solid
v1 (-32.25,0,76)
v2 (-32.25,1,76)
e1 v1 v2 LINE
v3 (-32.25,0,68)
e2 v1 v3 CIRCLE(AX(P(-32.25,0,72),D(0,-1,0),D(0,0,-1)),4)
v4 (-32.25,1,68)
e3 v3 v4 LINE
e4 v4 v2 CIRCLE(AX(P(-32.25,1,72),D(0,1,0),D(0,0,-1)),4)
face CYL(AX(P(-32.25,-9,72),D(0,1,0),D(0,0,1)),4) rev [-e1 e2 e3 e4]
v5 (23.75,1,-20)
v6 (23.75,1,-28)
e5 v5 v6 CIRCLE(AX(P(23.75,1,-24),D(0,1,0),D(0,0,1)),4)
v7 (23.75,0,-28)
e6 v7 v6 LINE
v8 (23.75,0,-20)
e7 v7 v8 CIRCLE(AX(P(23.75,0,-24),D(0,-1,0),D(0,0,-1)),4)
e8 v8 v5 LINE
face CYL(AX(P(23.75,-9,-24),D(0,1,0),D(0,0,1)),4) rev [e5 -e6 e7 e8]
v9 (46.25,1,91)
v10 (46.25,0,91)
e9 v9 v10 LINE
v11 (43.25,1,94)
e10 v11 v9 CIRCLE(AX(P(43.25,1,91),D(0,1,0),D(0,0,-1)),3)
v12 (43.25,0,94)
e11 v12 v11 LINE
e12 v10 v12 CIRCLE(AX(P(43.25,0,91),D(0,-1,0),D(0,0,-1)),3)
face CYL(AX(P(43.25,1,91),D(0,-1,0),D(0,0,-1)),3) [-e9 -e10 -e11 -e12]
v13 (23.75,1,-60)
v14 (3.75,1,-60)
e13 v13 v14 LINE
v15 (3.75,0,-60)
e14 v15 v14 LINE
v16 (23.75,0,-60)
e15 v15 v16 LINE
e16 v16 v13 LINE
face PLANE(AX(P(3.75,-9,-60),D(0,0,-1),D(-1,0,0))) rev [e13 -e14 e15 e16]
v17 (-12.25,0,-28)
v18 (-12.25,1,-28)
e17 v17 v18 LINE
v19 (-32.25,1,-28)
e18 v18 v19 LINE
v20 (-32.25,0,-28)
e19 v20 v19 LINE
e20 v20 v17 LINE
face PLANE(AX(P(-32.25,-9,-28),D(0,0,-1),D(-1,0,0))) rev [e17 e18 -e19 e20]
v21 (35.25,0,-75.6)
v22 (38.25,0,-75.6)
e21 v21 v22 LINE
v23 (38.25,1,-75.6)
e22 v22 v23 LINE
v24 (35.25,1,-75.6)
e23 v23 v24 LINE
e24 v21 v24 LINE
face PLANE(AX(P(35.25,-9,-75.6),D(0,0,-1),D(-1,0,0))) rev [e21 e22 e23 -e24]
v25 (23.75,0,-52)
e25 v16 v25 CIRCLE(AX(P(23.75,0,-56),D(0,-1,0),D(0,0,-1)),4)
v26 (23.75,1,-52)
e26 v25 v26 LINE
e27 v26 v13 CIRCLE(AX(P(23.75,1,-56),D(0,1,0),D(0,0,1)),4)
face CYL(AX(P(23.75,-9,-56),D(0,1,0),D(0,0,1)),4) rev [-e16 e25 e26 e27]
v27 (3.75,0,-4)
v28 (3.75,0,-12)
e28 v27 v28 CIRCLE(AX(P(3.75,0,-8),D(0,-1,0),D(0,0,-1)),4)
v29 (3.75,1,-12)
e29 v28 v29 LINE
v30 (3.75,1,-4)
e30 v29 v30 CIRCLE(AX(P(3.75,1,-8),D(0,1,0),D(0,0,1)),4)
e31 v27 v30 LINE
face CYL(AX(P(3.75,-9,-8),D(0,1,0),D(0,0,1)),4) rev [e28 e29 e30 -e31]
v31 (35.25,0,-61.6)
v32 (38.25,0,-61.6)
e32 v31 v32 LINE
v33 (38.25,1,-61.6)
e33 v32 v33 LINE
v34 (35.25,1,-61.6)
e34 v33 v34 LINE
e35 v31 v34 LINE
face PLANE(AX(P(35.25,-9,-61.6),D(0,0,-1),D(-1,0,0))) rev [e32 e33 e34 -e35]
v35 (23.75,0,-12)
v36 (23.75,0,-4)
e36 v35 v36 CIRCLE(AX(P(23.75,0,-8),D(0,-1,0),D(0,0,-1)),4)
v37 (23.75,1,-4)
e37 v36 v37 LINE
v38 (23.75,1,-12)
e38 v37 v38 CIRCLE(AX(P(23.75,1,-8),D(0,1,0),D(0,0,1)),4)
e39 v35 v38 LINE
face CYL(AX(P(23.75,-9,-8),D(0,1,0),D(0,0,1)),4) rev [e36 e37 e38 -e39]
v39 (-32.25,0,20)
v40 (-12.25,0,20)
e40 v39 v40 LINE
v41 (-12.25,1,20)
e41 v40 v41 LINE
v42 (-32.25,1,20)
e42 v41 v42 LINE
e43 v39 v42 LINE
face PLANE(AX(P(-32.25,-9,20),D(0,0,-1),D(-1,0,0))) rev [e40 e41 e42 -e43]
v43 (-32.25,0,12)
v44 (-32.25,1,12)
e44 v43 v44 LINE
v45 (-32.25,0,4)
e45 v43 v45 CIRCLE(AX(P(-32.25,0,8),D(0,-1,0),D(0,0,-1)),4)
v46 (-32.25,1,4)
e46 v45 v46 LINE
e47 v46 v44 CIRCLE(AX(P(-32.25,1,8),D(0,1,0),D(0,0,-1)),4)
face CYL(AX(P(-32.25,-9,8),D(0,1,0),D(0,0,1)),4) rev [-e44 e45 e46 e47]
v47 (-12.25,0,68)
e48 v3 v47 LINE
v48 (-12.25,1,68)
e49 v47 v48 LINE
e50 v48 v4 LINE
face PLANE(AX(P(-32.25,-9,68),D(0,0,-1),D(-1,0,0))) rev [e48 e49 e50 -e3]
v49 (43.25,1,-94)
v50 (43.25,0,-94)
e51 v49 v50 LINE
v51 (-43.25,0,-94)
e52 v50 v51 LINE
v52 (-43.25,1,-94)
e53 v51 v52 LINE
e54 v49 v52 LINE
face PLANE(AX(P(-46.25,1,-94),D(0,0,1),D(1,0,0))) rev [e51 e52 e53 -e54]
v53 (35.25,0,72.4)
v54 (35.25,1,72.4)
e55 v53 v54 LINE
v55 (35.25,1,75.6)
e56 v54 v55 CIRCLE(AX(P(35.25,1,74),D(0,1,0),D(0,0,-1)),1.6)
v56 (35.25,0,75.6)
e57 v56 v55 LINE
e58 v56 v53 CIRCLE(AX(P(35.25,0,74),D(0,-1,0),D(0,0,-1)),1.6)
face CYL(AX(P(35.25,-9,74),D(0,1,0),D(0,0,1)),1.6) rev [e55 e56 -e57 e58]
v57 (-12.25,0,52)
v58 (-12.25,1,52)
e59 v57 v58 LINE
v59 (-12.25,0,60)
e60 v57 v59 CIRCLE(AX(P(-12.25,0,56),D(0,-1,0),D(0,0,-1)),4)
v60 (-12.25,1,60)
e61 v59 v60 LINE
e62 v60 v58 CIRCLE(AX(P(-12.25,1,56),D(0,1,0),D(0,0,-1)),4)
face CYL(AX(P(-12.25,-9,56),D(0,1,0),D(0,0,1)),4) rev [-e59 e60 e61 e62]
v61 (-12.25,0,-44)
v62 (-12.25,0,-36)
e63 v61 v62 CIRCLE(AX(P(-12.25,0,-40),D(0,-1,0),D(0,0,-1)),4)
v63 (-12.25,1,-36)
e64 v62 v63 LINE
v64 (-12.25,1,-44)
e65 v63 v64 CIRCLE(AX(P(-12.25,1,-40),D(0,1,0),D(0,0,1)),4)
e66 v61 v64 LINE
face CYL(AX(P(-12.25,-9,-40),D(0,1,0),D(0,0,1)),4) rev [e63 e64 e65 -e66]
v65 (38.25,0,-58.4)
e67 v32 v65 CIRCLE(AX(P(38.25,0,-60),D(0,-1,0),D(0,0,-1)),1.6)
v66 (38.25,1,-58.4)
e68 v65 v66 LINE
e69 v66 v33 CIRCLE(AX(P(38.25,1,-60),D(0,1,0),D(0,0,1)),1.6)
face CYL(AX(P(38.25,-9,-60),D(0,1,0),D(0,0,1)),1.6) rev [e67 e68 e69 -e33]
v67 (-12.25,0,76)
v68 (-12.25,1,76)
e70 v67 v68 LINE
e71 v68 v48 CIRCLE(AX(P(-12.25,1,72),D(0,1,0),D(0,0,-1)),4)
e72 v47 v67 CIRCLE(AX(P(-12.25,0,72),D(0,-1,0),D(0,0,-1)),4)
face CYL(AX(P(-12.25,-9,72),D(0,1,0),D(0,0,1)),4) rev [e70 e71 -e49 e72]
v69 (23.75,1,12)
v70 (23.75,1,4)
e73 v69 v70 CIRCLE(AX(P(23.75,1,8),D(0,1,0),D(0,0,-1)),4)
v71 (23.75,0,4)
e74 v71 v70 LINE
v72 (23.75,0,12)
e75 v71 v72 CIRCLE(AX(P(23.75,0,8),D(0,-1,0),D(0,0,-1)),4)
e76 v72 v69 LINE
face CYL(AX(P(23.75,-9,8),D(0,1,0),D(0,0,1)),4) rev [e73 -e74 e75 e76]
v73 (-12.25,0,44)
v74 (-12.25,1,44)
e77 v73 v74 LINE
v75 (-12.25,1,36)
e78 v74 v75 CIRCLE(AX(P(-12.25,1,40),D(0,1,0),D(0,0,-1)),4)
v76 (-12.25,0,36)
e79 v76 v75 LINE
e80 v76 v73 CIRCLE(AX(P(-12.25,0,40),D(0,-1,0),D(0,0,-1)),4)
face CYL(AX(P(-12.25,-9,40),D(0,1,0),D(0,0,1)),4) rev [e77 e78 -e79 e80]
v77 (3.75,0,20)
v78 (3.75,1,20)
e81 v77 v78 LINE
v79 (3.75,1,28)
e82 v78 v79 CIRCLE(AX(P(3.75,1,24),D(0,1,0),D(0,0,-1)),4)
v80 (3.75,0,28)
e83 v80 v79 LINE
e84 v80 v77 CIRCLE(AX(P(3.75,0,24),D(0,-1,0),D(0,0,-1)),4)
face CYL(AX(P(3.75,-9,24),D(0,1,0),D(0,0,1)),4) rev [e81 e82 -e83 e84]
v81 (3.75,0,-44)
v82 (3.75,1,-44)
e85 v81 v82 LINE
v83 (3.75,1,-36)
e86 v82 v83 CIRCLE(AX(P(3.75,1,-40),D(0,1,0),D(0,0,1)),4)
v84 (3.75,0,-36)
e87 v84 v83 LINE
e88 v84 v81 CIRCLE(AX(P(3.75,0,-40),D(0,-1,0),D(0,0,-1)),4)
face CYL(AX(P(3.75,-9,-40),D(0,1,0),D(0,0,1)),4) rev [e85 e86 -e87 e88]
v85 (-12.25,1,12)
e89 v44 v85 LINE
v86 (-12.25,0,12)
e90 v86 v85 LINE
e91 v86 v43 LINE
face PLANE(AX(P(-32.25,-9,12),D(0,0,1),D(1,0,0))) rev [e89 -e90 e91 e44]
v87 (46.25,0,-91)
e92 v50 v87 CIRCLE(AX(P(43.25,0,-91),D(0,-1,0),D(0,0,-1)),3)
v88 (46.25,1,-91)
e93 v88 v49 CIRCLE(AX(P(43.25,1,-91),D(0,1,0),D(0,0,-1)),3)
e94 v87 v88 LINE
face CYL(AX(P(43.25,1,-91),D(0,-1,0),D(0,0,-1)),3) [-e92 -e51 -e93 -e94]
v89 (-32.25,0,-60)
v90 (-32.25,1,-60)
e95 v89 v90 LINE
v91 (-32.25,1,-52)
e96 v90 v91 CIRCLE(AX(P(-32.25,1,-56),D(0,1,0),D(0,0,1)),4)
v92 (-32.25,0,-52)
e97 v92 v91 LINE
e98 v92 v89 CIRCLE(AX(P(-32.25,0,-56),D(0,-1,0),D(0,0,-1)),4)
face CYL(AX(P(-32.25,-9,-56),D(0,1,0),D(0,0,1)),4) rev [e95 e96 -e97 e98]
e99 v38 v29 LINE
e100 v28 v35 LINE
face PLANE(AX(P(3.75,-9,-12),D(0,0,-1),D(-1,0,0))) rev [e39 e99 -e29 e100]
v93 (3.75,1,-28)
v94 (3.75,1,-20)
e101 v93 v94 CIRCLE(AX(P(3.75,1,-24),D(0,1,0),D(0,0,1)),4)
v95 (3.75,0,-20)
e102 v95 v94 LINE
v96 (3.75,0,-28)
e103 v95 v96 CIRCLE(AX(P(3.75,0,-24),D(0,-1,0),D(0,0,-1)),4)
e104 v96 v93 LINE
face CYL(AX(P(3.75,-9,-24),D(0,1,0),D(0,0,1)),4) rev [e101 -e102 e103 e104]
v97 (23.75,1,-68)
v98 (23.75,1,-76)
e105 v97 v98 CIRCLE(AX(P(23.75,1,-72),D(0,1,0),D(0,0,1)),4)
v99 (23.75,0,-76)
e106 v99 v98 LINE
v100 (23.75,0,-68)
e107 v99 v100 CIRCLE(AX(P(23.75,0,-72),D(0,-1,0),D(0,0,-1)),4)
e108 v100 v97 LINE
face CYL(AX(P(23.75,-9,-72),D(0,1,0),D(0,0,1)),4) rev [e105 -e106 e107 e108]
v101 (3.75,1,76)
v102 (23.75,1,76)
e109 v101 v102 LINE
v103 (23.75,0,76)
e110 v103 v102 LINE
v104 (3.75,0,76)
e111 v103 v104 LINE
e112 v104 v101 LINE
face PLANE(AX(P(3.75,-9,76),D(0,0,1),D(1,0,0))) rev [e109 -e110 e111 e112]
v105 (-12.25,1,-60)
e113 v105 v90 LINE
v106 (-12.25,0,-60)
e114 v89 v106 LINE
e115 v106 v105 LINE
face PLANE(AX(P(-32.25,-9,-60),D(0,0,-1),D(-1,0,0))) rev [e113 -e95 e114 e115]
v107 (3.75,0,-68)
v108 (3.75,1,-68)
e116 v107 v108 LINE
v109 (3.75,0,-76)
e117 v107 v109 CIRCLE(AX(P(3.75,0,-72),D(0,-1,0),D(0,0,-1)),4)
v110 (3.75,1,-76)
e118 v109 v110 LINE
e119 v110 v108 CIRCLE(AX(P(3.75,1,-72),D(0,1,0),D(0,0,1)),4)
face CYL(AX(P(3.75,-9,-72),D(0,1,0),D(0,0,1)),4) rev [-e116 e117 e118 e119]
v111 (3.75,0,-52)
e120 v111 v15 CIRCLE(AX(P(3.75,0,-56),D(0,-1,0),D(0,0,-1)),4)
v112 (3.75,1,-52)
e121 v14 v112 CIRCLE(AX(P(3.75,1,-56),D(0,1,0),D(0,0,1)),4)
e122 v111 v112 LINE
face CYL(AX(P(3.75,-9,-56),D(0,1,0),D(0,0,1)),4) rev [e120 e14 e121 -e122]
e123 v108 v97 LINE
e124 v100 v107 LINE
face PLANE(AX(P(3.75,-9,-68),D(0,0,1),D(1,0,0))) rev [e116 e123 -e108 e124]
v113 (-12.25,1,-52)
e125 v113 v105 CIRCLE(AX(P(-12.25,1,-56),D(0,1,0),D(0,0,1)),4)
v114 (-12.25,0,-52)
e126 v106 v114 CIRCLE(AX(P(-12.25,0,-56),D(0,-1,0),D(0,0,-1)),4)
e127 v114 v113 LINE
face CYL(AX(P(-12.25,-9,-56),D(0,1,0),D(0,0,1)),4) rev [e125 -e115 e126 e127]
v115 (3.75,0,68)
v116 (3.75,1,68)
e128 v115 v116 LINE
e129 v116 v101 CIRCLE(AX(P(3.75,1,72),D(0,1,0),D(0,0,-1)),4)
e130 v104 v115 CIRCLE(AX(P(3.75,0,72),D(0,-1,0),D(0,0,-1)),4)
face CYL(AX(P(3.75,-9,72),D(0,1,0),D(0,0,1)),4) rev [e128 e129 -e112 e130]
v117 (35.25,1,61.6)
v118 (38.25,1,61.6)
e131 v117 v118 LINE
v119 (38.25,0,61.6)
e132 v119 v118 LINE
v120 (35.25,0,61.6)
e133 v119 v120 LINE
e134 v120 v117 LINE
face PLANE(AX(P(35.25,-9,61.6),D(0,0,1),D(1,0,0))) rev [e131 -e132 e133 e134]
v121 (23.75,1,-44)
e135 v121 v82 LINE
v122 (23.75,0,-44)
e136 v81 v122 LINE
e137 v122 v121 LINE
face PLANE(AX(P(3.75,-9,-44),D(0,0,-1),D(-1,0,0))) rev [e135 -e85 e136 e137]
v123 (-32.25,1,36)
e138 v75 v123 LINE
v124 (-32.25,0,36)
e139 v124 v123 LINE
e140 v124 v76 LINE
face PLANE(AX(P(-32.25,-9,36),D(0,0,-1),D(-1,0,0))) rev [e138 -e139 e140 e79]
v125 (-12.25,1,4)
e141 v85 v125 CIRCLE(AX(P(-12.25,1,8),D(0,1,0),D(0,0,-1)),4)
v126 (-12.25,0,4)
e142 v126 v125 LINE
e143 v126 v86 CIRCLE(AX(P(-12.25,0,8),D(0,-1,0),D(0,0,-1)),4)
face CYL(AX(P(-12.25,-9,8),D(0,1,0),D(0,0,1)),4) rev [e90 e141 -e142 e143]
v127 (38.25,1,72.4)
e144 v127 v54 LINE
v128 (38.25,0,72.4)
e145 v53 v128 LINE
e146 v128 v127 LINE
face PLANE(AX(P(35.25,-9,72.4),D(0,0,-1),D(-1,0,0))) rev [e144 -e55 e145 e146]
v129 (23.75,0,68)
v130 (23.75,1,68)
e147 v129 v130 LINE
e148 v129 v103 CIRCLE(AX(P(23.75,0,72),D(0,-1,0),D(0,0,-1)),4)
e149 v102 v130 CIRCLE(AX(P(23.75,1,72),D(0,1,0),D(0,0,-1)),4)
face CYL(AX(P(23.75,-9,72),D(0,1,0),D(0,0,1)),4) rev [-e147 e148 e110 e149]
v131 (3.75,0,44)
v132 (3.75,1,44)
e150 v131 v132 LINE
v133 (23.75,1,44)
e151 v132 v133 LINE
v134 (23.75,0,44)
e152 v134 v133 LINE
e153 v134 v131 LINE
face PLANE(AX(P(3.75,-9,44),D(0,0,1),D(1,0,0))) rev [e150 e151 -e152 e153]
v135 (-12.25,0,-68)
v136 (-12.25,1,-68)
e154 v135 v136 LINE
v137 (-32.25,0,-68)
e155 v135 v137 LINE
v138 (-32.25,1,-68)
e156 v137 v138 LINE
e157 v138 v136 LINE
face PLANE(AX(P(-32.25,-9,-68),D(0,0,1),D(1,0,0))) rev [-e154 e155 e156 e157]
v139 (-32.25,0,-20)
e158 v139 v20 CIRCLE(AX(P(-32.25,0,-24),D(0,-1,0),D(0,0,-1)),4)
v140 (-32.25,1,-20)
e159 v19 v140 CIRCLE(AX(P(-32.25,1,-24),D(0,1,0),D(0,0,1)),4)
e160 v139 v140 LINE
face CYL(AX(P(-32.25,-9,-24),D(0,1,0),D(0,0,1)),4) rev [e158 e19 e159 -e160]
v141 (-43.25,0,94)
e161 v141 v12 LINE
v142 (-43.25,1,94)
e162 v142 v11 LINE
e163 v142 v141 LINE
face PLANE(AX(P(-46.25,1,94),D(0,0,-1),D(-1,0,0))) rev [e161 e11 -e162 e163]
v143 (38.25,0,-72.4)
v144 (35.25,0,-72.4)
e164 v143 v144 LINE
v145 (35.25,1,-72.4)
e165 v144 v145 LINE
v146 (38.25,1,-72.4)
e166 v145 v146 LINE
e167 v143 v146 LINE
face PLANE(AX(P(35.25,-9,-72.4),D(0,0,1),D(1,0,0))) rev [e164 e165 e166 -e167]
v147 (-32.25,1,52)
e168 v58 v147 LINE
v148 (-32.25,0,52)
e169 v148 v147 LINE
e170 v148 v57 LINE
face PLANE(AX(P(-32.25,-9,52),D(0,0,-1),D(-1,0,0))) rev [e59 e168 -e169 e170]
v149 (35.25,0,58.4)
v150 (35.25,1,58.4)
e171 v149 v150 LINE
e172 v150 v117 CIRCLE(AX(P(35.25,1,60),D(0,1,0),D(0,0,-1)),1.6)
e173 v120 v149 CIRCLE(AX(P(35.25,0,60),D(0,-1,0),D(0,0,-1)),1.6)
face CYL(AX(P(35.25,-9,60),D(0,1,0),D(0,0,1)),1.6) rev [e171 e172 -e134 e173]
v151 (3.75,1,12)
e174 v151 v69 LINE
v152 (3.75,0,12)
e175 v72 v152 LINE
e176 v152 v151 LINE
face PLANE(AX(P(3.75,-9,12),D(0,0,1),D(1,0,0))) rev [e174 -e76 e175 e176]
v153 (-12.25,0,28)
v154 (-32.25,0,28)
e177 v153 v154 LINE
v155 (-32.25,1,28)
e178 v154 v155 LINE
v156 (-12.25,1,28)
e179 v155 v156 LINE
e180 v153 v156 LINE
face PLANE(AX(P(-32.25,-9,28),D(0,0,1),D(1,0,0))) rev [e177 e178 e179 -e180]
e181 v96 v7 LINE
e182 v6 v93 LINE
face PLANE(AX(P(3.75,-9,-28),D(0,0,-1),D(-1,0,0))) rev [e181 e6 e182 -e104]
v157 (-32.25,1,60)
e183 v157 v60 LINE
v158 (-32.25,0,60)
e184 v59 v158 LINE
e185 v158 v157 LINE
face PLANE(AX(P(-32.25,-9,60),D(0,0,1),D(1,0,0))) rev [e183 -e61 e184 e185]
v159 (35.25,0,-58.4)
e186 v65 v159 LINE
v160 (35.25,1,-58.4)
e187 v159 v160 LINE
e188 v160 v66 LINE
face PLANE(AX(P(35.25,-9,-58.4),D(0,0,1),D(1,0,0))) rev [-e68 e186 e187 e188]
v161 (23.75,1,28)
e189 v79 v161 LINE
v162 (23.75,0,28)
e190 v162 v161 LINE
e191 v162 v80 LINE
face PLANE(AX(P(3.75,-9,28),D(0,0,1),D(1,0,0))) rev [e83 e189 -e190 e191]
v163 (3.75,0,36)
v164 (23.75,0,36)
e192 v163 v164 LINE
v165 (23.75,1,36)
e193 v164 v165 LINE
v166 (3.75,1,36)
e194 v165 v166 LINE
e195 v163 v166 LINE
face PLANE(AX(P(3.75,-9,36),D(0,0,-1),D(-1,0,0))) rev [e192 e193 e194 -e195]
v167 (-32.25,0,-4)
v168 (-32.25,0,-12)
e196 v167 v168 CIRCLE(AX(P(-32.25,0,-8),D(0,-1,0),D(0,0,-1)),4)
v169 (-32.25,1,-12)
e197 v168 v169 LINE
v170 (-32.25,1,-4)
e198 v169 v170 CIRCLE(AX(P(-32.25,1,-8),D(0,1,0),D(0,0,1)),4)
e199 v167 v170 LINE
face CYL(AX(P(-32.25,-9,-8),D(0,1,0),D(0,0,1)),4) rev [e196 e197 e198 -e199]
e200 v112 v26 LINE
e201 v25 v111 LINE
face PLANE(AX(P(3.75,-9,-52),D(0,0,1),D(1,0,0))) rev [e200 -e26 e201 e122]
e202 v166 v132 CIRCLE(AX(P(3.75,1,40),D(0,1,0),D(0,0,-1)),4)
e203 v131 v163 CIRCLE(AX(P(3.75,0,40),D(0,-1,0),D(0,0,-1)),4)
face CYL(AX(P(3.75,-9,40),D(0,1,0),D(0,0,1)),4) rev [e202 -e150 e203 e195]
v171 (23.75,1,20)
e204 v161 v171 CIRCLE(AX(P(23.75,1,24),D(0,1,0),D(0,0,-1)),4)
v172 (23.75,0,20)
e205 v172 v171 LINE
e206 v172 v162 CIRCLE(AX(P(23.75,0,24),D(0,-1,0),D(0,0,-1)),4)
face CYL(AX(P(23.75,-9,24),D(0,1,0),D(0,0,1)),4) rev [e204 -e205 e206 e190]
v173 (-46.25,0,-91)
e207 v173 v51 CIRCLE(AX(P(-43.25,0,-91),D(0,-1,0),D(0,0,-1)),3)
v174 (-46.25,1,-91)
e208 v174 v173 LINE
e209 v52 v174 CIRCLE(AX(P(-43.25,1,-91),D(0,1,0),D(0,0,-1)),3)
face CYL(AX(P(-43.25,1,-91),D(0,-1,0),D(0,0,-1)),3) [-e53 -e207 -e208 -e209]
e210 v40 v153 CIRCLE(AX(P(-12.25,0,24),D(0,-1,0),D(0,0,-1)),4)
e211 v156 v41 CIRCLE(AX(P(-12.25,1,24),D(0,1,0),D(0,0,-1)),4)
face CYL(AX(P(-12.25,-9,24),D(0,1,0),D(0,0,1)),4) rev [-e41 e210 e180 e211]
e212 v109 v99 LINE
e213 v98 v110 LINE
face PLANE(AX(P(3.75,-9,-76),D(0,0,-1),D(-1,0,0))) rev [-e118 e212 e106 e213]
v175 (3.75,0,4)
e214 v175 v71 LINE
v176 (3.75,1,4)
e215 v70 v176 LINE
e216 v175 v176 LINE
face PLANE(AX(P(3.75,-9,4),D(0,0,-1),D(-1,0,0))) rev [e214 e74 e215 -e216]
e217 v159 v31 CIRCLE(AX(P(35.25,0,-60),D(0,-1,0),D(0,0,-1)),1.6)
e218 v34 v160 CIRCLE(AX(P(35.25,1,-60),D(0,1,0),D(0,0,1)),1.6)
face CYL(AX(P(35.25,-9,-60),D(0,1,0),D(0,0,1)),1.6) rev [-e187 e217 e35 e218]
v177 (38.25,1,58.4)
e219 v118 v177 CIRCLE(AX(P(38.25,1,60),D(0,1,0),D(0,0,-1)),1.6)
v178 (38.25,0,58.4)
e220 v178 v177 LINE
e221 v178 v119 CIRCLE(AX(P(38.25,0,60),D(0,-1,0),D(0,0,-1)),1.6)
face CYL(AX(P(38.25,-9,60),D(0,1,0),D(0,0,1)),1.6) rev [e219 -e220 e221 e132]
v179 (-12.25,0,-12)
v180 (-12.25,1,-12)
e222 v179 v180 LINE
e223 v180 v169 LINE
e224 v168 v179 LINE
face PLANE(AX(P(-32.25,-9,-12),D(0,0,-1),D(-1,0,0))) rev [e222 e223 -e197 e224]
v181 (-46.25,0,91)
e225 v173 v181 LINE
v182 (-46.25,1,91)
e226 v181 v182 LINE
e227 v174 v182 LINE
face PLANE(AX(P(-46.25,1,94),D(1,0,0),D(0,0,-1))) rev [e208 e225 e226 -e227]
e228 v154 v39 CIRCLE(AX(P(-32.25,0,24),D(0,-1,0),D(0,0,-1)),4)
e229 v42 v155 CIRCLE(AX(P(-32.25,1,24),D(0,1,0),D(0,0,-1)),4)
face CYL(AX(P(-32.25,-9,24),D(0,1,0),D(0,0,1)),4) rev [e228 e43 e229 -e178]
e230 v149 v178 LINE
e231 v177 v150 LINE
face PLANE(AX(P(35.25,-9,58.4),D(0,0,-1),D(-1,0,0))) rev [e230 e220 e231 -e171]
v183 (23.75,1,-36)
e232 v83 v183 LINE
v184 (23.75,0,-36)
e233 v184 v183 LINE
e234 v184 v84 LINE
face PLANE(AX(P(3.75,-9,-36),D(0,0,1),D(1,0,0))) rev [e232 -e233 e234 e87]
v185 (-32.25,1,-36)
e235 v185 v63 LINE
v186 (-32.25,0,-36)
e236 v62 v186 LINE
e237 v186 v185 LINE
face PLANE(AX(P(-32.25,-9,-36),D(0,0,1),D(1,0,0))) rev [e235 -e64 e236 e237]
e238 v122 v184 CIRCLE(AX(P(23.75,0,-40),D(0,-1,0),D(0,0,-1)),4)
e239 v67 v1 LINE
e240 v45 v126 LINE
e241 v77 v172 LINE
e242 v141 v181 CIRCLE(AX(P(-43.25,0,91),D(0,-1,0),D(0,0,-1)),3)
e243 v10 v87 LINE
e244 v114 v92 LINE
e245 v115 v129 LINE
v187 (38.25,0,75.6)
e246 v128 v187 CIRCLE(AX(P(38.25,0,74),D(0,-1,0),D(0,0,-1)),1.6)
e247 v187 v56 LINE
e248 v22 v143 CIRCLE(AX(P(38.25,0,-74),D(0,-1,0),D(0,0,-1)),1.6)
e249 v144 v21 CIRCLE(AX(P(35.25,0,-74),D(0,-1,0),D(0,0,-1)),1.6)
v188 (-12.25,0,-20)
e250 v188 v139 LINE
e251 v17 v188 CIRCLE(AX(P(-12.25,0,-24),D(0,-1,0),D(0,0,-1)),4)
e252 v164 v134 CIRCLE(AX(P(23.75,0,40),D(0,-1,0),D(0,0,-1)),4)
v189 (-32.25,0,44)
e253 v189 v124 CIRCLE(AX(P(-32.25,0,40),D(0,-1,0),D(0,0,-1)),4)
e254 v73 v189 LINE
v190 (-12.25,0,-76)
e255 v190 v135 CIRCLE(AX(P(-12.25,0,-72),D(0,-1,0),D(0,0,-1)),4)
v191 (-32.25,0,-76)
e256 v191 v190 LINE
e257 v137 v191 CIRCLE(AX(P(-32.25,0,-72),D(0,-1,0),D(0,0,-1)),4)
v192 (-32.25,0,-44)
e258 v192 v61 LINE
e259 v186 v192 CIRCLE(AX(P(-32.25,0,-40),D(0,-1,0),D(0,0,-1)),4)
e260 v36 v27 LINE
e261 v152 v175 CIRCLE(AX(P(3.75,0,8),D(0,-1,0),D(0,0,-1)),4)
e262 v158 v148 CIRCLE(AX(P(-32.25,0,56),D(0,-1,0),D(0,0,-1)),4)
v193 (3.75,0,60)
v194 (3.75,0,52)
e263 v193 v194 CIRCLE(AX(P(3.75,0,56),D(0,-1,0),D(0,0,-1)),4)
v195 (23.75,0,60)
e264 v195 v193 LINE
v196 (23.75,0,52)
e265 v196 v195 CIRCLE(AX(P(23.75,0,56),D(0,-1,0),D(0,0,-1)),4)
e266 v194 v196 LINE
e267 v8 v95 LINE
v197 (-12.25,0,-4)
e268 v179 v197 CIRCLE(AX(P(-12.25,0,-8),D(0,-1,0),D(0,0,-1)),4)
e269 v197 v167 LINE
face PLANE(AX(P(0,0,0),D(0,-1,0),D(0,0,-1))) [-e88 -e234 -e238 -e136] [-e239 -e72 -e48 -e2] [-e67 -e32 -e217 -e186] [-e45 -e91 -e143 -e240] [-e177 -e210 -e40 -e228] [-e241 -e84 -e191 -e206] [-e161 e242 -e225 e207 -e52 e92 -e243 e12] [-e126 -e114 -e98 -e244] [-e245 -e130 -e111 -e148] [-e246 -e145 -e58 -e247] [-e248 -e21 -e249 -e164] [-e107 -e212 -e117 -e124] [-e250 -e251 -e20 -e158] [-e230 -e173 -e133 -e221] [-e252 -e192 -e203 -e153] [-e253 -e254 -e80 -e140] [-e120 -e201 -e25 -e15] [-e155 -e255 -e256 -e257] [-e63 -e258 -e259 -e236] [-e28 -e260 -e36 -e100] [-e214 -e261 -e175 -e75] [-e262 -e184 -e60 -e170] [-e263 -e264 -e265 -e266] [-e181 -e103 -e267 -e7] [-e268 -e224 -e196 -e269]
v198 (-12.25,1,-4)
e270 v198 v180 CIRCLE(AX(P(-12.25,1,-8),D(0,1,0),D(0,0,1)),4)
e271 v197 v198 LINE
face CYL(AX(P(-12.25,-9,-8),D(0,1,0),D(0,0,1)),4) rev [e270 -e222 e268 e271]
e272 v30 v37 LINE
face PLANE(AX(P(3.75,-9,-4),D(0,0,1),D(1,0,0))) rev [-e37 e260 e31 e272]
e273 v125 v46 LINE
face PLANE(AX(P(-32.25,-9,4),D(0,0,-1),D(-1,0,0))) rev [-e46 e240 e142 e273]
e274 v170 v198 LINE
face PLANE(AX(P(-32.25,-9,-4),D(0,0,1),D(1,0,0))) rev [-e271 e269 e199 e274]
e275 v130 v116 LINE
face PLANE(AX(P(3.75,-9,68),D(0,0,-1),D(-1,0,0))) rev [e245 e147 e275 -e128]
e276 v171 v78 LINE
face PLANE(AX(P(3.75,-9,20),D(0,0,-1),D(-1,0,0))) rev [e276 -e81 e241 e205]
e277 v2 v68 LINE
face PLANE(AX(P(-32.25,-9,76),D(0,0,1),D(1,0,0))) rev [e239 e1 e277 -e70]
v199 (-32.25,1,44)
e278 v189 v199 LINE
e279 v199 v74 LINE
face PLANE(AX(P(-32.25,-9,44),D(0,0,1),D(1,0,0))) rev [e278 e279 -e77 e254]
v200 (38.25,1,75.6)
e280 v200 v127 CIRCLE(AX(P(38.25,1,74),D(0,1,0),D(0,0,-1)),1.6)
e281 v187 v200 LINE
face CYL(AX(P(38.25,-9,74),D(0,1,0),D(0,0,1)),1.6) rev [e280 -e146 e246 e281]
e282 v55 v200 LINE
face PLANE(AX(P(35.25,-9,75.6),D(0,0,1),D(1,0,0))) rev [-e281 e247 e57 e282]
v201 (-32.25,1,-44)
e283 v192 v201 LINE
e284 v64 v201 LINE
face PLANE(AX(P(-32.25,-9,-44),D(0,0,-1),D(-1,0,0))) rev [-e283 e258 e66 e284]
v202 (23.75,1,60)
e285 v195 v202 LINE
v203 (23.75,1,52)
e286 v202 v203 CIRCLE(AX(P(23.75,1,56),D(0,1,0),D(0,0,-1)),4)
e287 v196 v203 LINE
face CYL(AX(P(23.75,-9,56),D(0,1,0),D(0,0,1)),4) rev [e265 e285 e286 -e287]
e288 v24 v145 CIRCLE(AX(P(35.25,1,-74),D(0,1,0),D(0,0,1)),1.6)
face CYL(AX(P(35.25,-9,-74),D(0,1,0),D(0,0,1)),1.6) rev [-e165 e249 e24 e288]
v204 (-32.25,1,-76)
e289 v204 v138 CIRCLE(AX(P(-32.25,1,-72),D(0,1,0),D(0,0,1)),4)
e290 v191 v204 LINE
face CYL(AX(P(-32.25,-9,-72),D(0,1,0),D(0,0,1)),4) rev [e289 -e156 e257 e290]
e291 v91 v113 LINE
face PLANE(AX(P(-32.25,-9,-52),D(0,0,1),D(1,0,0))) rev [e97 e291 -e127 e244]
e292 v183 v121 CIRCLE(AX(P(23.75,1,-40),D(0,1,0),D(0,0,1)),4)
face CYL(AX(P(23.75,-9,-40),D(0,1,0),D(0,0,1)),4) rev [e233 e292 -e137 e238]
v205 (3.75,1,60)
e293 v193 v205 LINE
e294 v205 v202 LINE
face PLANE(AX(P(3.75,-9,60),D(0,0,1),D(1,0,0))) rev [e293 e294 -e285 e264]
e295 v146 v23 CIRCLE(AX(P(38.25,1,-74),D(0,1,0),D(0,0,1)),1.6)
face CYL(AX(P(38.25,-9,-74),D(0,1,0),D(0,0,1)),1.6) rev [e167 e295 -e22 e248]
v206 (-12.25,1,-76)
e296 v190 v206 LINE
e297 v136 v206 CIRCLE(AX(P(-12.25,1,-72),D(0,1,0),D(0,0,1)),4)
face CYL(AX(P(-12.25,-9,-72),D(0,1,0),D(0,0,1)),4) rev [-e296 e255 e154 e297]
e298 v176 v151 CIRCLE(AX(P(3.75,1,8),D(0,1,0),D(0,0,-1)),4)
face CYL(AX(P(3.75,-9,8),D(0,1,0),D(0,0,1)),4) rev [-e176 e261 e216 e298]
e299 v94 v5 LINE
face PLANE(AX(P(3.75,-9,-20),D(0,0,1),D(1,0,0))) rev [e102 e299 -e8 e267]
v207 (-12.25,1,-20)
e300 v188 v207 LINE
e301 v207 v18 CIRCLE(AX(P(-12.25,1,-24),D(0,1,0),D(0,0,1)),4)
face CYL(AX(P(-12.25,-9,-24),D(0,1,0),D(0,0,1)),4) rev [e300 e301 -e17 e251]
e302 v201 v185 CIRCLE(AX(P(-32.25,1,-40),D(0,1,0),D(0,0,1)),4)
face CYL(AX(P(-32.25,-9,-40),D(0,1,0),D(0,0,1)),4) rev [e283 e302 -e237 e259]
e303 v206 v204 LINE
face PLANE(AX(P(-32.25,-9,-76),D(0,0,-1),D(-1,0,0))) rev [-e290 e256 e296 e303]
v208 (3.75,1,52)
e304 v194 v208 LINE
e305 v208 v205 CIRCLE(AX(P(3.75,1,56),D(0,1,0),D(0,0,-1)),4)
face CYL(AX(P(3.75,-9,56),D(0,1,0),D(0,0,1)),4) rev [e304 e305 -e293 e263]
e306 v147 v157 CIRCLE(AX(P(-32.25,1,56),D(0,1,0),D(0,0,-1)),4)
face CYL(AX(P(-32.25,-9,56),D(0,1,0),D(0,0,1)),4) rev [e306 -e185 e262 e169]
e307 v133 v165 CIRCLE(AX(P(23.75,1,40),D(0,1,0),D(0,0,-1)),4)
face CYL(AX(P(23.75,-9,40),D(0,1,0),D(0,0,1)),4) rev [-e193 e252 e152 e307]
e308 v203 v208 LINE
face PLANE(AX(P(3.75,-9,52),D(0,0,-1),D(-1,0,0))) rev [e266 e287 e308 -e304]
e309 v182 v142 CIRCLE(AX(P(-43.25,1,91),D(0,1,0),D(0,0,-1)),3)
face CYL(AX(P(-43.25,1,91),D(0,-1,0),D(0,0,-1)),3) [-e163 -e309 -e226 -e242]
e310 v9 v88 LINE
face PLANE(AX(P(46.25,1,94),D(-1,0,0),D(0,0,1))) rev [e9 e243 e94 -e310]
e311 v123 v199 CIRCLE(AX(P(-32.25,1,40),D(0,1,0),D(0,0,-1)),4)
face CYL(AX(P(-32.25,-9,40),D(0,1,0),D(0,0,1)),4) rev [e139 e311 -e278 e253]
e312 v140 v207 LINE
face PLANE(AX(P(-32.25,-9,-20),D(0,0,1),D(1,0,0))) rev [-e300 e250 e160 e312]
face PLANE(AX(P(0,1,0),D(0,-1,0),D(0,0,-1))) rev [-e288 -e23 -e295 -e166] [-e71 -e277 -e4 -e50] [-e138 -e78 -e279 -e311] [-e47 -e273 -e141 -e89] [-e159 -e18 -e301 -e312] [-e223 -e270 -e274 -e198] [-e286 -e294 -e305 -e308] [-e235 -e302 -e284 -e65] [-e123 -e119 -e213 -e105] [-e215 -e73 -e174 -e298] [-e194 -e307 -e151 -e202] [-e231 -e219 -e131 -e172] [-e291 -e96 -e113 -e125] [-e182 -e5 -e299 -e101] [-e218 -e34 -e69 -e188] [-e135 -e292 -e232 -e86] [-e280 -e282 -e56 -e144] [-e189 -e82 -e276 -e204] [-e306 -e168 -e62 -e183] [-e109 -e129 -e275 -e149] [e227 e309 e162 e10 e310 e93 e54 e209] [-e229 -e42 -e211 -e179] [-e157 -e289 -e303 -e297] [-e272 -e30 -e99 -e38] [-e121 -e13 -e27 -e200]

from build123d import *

# Parameters (mm, degrees)
SKETCH_1_W          = 92.5
SKETCH_1_H          = 188
EXTRUDE_1_DEPTH     = 1
FILLET_1_R          = 3
CUT_EXTRUDE_2_DEPTH = 10
CUT_EXTRUDE_3_DEPTH = 10


with BuildPart() as part:
    # 草图1 → 凸台-拉伸1 (new body)
    with BuildSketch(Plane(origin=(0, 0, 0), x_dir=(1, 0, 0), z_dir=(0, 1, 0))):
        Rectangle(SKETCH_1_W, SKETCH_1_H)
    extrude(amount=EXTRUDE_1_DEPTH)

    # 圆角1
    fillet_1_edges = [part.edges().sort_by_distance(p)[0] for p in [
        (46.25, 0.5, 94),
        (-46.25, 0.5, 94),
        (-46.25, 0.5, -94),
        (46.25, 0.5, -94),
    ]]
    fillet(fillet_1_edges, radius=FILLET_1_R)

    # 草图3 → 切除-拉伸2 (cut)
    with BuildSketch(Plane(origin=(0, 1, 0), x_dir=(1, 0, 0), z_dir=(0, 1, 0))):
        with BuildLine():
            Line((35.25, 61.6), (38.25, 61.6))
            ThreePointArc((38.25, 61.6), (39.85, 60), (38.25, 58.4))
            Line((38.25, 58.4), (35.25, 58.4))
            ThreePointArc((35.25, 58.4), (33.65, 60), (35.25, 61.6))
        make_face()
        with BuildLine():
            Line((35.25, 75.6), (38.25, 75.6))
            ThreePointArc((38.25, 75.6), (39.85, 74), (38.25, 72.4))
            Line((38.25, 72.4), (35.25, 72.4))
            ThreePointArc((35.25, 72.4), (33.65, 74), (35.25, 75.6))
        make_face()
        with BuildLine():
            Line((35.25, -61.6), (38.25, -61.6))
            ThreePointArc((38.25, -61.6), (39.85, -60), (38.25, -58.4))
            Line((38.25, -58.4), (35.25, -58.4))
            ThreePointArc((35.25, -58.4), (33.65, -60), (35.25, -61.6))
        make_face()
        with BuildLine():
            Line((35.25, -75.6), (38.25, -75.6))
            ThreePointArc((38.25, -75.6), (39.85, -74), (38.25, -72.4))
            Line((38.25, -72.4), (35.25, -72.4))
            ThreePointArc((35.25, -72.4), (33.65, -74), (35.25, -75.6))
        make_face()
    extrude(amount=-CUT_EXTRUDE_2_DEPTH, mode=Mode.SUBTRACT)

    # 草图4 → 切除-拉伸3 (cut)
    with BuildSketch(Plane(origin=(0, 1, 0), x_dir=(1, 0, 0), z_dir=(0, 1, 0))):
        with BuildLine():
            Line((-32.25, 12), (-12.25, 12))
            ThreePointArc((-12.25, 12), (-8.25, 8), (-12.25, 4))
            Line((-12.25, 4), (-32.25, 4))
            ThreePointArc((-32.25, 4), (-36.25, 8), (-32.25, 12))
        make_face()
        with BuildLine():
            Line((3.75, 12), (23.75, 12))
            ThreePointArc((23.75, 12), (27.75, 8), (23.75, 4))
            Line((23.75, 4), (3.75, 4))
            ThreePointArc((3.75, 4), (-0.25, 8), (3.75, 12))
        make_face()
        with BuildLine():
            Line((-32.25, 28), (-12.25, 28))
            ThreePointArc((-12.25, 28), (-8.25, 24), (-12.25, 20))
            Line((-12.25, 20), (-32.25, 20))
            ThreePointArc((-32.25, 20), (-36.25, 24), (-32.25, 28))
        make_face()
        with BuildLine():
            Line((3.75, 28), (23.75, 28))
            ThreePointArc((23.75, 28), (27.75, 24), (23.75, 20))
            Line((23.75, 20), (3.75, 20))
            ThreePointArc((3.75, 20), (-0.25, 24), (3.75, 28))
        make_face()
        with BuildLine():
            Line((-32.25, 44), (-12.25, 44))
            ThreePointArc((-12.25, 44), (-8.25, 40), (-12.25, 36))
            Line((-12.25, 36), (-32.25, 36))
            ThreePointArc((-32.25, 36), (-36.25, 40), (-32.25, 44))
        make_face()
        with BuildLine():
            Line((3.75, 44), (23.75, 44))
            ThreePointArc((23.75, 44), (27.75, 40), (23.75, 36))
            Line((23.75, 36), (3.75, 36))
            ThreePointArc((3.75, 36), (-0.25, 40), (3.75, 44))
        make_face()
        with BuildLine():
            Line((-32.25, 60), (-12.25, 60))
            ThreePointArc((-12.25, 60), (-8.25, 56), (-12.25, 52))
            Line((-12.25, 52), (-32.25, 52))
            ThreePointArc((-32.25, 52), (-36.25, 56), (-32.25, 60))
        make_face()
        with BuildLine():
            Line((3.75, 60), (23.75, 60))
            ThreePointArc((23.75, 60), (27.75, 56), (23.75, 52))
            Line((23.75, 52), (3.75, 52))
            ThreePointArc((3.75, 52), (-0.25, 56), (3.75, 60))
        make_face()
        with BuildLine():
            Line((-32.25, 76), (-12.25, 76))
            ThreePointArc((-12.25, 76), (-8.25, 72), (-12.25, 68))
            Line((-12.25, 68), (-32.25, 68))
            ThreePointArc((-32.25, 68), (-36.25, 72), (-32.25, 76))
        make_face()
        with BuildLine():
            Line((3.75, 76), (23.75, 76))
            ThreePointArc((23.75, 76), (27.75, 72), (23.75, 68))
            Line((23.75, 68), (3.75, 68))
            ThreePointArc((3.75, 68), (-0.25, 72), (3.75, 76))
        make_face()
        with BuildLine():
            Line((3.75, -76), (23.75, -76))
            ThreePointArc((23.75, -76), (27.75, -72), (23.75, -68))
            Line((23.75, -68), (3.75, -68))
            ThreePointArc((3.75, -68), (-0.25, -72), (3.75, -76))
        make_face()
        with BuildLine():
            Line((-32.25, -76), (-12.25, -76))
            ThreePointArc((-12.25, -76), (-8.25, -72), (-12.25, -68))
            Line((-12.25, -68), (-32.25, -68))
            ThreePointArc((-32.25, -68), (-36.25, -72), (-32.25, -76))
        make_face()
        with BuildLine():
            Line((3.75, -60), (23.75, -60))
            ThreePointArc((23.75, -60), (27.75, -56), (23.75, -52))
            Line((23.75, -52), (3.75, -52))
            ThreePointArc((3.75, -52), (-0.25, -56), (3.75, -60))
        make_face()
        with BuildLine():
            Line((-32.25, -60), (-12.25, -60))
            ThreePointArc((-12.25, -60), (-8.25, -56), (-12.25, -52))
            Line((-12.25, -52), (-32.25, -52))
            ThreePointArc((-32.25, -52), (-36.25, -56), (-32.25, -60))
        make_face()
        with BuildLine():
            Line((3.75, -44), (23.75, -44))
            ThreePointArc((23.75, -44), (27.75, -40), (23.75, -36))
            Line((23.75, -36), (3.75, -36))
            ThreePointArc((3.75, -36), (-0.25, -40), (3.75, -44))
        make_face()
        with BuildLine():
            Line((-32.25, -44), (-12.25, -44))
            ThreePointArc((-12.25, -44), (-8.25, -40), (-12.25, -36))
            Line((-12.25, -36), (-32.25, -36))
            ThreePointArc((-32.25, -36), (-36.25, -40), (-32.25, -44))
        make_face()
        with BuildLine():
            Line((3.75, -28), (23.75, -28))
            ThreePointArc((23.75, -28), (27.75, -24), (23.75, -20))
            Line((23.75, -20), (3.75, -20))
            ThreePointArc((3.75, -20), (-0.25, -24), (3.75, -28))
        make_face()
        with BuildLine():
            Line((-32.25, -28), (-12.25, -28))
            ThreePointArc((-12.25, -28), (-8.25, -24), (-12.25, -20))
            Line((-12.25, -20), (-32.25, -20))
            ThreePointArc((-32.25, -20), (-36.25, -24), (-32.25, -28))
        make_face()
        with BuildLine():
            Line((3.75, -12), (23.75, -12))
            ThreePointArc((23.75, -12), (27.75, -8), (23.75, -4))
            Line((23.75, -4), (3.75, -4))
            ThreePointArc((3.75, -4), (-0.25, -8), (3.75, -12))
        make_face()
        with BuildLine():
            Line((-32.25, -12), (-12.25, -12))
            ThreePointArc((-12.25, -12), (-8.25, -8), (-12.25, -4))
            Line((-12.25, -4), (-32.25, -4))
            ThreePointArc((-32.25, -4), (-36.25, -8), (-32.25, -12))
        make_face()
    extrude(amount=-CUT_EXTRUDE_3_DEPTH, mode=Mode.SUBTRACT)


solid = part.part
